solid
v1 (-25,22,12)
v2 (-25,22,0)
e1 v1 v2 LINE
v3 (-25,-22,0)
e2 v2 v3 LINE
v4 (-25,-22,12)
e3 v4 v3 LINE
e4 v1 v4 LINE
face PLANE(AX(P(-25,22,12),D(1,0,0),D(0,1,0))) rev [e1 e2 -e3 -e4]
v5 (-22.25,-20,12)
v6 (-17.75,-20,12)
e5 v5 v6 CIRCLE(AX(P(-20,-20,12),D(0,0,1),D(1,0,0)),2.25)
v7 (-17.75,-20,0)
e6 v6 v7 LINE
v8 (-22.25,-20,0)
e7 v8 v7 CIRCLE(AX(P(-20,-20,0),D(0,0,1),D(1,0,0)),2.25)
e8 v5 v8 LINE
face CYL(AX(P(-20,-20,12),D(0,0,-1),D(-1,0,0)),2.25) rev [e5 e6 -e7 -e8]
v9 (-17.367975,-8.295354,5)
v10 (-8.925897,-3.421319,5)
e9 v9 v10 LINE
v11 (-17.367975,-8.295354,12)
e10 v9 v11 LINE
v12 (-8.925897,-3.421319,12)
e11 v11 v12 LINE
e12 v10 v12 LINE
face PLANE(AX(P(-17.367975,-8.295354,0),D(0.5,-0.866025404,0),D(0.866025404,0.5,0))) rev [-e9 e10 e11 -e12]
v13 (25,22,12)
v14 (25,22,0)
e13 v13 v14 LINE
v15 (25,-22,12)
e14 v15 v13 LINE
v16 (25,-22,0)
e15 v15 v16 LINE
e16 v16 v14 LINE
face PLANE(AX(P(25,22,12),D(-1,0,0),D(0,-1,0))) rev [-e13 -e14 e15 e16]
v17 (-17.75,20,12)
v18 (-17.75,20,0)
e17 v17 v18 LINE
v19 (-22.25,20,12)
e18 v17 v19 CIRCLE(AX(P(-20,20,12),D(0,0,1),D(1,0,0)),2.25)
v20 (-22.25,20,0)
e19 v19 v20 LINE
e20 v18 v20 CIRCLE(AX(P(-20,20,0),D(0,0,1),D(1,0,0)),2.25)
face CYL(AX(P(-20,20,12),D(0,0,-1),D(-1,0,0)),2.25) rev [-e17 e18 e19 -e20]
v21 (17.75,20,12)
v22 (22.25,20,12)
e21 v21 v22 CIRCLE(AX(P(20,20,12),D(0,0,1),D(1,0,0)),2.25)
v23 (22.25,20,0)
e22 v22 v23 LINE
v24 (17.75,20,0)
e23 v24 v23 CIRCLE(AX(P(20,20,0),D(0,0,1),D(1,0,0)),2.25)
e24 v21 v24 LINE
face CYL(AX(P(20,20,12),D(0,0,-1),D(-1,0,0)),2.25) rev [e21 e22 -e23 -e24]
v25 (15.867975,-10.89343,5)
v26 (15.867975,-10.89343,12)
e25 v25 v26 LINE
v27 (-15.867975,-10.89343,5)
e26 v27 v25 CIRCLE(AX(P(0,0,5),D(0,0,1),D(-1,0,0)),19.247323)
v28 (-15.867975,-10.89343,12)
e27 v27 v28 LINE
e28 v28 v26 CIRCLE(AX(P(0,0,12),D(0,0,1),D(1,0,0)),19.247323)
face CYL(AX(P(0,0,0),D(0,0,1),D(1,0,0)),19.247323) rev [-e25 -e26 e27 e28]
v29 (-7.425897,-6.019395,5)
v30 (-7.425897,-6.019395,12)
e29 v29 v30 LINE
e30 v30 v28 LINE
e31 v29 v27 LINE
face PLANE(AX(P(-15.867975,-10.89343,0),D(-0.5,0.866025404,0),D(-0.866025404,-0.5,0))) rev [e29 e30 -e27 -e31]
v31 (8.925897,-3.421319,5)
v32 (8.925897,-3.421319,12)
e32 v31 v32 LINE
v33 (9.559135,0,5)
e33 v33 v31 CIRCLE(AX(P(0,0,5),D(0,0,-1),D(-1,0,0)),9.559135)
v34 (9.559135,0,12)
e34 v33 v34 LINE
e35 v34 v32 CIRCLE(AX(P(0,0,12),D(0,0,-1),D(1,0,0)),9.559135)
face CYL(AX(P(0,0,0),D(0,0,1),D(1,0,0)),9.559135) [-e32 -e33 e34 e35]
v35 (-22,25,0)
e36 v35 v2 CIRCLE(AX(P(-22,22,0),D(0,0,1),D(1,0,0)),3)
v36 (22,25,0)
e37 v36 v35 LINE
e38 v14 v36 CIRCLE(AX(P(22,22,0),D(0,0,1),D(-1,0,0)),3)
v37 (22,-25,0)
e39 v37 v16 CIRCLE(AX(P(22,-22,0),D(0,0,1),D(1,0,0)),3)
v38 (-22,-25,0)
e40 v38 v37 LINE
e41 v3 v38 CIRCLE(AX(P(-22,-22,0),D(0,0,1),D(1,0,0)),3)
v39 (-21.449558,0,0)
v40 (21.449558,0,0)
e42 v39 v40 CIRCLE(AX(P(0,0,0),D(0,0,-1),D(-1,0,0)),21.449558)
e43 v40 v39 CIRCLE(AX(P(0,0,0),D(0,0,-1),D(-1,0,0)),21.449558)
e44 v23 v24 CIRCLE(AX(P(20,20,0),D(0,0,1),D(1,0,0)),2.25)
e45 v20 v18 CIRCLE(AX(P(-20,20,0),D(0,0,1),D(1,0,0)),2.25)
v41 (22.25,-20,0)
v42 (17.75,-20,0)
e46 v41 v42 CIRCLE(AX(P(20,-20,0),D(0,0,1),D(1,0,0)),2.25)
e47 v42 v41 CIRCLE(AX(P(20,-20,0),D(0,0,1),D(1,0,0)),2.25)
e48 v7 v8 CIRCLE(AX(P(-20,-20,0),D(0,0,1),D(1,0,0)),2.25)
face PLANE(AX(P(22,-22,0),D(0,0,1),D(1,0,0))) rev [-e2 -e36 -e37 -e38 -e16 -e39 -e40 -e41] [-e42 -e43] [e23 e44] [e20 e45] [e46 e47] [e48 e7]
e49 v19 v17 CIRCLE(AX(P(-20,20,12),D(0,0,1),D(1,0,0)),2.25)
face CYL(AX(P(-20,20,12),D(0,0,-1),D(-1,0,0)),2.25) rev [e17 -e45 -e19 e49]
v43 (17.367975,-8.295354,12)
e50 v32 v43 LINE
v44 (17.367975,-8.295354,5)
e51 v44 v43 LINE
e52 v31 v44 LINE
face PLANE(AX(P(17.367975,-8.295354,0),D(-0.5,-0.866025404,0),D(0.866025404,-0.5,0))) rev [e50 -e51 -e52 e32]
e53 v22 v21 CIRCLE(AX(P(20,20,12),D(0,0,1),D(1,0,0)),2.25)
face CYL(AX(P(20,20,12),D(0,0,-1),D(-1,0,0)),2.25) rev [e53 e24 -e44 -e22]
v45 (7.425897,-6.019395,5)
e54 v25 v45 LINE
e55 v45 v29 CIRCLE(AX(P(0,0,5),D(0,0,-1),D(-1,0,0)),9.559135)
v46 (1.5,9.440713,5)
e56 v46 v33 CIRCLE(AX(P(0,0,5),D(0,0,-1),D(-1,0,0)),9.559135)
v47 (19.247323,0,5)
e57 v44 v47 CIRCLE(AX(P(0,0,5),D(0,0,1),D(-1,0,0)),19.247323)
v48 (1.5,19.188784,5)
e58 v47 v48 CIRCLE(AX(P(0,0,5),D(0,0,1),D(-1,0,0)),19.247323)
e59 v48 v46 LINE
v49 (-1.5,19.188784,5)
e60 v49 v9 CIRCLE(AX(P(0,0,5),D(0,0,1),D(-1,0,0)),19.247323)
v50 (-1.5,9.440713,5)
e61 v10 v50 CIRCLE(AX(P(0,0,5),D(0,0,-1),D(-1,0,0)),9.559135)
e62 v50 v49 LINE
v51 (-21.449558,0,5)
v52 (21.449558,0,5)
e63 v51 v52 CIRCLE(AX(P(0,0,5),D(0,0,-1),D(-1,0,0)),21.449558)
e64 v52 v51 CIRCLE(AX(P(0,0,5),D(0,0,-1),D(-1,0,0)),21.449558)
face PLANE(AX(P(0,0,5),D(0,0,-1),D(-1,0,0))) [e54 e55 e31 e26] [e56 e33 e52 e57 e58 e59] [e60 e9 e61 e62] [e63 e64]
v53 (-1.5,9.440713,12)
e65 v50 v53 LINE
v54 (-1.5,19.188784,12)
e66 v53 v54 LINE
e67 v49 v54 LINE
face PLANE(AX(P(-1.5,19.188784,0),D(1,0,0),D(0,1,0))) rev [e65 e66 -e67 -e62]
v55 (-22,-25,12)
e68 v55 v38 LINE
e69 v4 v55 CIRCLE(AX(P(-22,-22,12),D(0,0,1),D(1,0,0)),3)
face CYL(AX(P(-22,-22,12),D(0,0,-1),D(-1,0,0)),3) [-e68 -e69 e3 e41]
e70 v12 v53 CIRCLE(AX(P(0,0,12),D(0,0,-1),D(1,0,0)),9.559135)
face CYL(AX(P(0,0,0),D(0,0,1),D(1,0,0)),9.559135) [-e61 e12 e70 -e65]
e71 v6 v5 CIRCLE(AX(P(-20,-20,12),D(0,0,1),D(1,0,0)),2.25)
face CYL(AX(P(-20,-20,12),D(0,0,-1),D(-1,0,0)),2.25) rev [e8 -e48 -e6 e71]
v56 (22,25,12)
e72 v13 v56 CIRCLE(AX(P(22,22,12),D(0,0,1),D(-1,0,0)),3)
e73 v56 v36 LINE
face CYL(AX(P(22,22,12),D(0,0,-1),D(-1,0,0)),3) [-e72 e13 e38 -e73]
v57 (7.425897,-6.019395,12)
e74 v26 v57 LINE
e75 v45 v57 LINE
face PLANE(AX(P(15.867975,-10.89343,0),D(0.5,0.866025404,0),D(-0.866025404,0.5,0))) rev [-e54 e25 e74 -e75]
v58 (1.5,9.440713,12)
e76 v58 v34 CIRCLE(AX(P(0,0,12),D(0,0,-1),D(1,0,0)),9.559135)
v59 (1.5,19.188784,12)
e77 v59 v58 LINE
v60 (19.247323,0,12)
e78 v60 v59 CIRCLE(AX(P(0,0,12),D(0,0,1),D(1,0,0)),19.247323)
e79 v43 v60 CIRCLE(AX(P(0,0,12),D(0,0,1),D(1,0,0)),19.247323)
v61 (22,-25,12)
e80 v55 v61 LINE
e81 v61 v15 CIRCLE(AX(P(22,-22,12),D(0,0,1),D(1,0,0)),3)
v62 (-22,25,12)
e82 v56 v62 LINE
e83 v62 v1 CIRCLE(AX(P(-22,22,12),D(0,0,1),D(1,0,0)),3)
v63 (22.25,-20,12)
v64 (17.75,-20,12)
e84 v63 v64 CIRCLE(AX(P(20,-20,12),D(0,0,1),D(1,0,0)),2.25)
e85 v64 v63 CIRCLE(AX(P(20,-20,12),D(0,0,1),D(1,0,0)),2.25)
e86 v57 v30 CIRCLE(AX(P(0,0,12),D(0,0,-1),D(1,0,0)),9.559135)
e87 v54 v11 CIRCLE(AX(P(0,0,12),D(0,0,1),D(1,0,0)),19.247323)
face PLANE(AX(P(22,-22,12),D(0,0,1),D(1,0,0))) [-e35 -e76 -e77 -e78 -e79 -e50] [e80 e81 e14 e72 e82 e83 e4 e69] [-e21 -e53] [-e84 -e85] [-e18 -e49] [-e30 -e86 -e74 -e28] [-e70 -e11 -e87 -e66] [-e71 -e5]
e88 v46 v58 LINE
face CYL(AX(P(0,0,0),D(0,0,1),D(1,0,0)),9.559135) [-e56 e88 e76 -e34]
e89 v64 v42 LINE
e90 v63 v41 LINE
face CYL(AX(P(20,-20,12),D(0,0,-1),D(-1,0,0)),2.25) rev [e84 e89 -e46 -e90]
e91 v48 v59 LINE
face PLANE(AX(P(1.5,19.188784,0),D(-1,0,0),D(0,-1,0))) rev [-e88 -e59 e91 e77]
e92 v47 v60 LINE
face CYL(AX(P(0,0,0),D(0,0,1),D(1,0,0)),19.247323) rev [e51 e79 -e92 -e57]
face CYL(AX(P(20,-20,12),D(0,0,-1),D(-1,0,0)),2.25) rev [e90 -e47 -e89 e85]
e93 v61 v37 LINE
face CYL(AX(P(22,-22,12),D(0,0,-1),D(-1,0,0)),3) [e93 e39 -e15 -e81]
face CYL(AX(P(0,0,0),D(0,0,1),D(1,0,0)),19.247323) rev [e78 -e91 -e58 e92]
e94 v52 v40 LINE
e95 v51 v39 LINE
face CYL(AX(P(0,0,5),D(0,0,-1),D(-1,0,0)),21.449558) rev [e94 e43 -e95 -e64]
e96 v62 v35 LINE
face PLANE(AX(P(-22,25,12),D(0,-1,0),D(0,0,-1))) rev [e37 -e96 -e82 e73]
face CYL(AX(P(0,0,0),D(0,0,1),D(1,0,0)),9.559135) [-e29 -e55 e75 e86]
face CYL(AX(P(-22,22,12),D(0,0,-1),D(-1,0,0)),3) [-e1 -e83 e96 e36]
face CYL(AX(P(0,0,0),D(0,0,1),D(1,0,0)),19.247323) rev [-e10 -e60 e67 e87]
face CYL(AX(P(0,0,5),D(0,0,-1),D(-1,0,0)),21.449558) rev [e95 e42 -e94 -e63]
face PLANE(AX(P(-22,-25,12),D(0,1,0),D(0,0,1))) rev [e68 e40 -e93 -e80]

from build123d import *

# Parameters (mm, degrees)
SKETCH1_R           = 2.25
BOSS_EXTRUDE1_DEPTH = 12
CUT_EXTRUDE1_DEPTH  = 12
SKETCH3_R           = 21.449558408
CUT_EXTRUDE2_DEPTH  = 5


with BuildPart() as part:
    # Sketch1 → Boss-Extrude1 (new body)
    with BuildSketch(Plane.XY):
        with BuildLine():
            Line((-22, 25), (22, 25))
            ThreePointArc((22, 25), (24.121320344, 24.121320344), (25, 22))
            Line((25, 22), (25, -22))
            ThreePointArc((25, -22), (24.121320344, -24.121320344), (22, -25))
            Line((22, -25), (-22, -25))
            ThreePointArc((-22, -25), (-24.121320344, -24.121320344), (-25, -22))
            Line((-25, -22), (-25, 22))
            ThreePointArc((-25, 22), (-24.121320344, 24.121320344), (-22, 25))
        make_face()
        with Locations((-20, 20)):
            Circle(SKETCH1_R, mode=Mode.SUBTRACT)
        with Locations((20, 20)):
            Circle(SKETCH1_R, mode=Mode.SUBTRACT)
        with Locations((20, -20)):
            Circle(SKETCH1_R, mode=Mode.SUBTRACT)
        with Locations((-20, -20)):
            Circle(SKETCH1_R, mode=Mode.SUBTRACT)
    extrude(amount=BOSS_EXTRUDE1_DEPTH)

    # Sketch2 → Cut-Extrude1 (cut)
    with BuildSketch(Plane.XY.offset(12)):
        with BuildLine():
            Line((-1.5, 19.188784117), (-1.5, 9.440713214))
            ThreePointArc((-1.5, 9.440713214), (-8.278453932, 4.779567606), (-8.925897474, -3.421318502))
            Line((-8.925897474, -3.421318502), (-17.367974513, -8.295353953))
            ThreePointArc((-17.367974513, -8.295353953), (-16.668670521, 9.623661412), (-1.5, 19.188784117))
        make_face()
        with BuildLine():
            Line((1.5, 19.188784117), (1.5, 9.440713214))
            ThreePointArc((1.5, 9.440713214), (8.278453932, 4.779567606), (8.925897474, -3.421318502))
            Line((8.925897474, -3.421318502), (17.367974513, -8.295353953))
            ThreePointArc((17.367974513, -8.295353953), (16.668670521, 9.623661412), (1.5, 19.188784117))
        make_face()
        with BuildLine():
            Line((15.867974513, -10.893430164), (7.425897474, -6.019394713))
            ThreePointArc((7.425897474, -6.019394713), (0, -9.559135212), (-7.425897474, -6.019394713))
            Line((-7.425897474, -6.019394713), (-15.867974513, -10.893430164))
            ThreePointArc((-15.867974513, -10.893430164), (0, -19.247322824), (15.867974513, -10.893430164))
        make_face()
    extrude(amount=-CUT_EXTRUDE1_DEPTH, mode=Mode.SUBTRACT)

    # Sketch3 → Cut-Extrude2 (cut)
    with BuildSketch(Plane(origin=(0, 0, 0), x_dir=(-1, 0, 0), z_dir=(0, 0, -1))):
        Circle(SKETCH3_R)
    extrude(amount=-CUT_EXTRUDE2_DEPTH, mode=Mode.SUBTRACT)


solid = part.part
